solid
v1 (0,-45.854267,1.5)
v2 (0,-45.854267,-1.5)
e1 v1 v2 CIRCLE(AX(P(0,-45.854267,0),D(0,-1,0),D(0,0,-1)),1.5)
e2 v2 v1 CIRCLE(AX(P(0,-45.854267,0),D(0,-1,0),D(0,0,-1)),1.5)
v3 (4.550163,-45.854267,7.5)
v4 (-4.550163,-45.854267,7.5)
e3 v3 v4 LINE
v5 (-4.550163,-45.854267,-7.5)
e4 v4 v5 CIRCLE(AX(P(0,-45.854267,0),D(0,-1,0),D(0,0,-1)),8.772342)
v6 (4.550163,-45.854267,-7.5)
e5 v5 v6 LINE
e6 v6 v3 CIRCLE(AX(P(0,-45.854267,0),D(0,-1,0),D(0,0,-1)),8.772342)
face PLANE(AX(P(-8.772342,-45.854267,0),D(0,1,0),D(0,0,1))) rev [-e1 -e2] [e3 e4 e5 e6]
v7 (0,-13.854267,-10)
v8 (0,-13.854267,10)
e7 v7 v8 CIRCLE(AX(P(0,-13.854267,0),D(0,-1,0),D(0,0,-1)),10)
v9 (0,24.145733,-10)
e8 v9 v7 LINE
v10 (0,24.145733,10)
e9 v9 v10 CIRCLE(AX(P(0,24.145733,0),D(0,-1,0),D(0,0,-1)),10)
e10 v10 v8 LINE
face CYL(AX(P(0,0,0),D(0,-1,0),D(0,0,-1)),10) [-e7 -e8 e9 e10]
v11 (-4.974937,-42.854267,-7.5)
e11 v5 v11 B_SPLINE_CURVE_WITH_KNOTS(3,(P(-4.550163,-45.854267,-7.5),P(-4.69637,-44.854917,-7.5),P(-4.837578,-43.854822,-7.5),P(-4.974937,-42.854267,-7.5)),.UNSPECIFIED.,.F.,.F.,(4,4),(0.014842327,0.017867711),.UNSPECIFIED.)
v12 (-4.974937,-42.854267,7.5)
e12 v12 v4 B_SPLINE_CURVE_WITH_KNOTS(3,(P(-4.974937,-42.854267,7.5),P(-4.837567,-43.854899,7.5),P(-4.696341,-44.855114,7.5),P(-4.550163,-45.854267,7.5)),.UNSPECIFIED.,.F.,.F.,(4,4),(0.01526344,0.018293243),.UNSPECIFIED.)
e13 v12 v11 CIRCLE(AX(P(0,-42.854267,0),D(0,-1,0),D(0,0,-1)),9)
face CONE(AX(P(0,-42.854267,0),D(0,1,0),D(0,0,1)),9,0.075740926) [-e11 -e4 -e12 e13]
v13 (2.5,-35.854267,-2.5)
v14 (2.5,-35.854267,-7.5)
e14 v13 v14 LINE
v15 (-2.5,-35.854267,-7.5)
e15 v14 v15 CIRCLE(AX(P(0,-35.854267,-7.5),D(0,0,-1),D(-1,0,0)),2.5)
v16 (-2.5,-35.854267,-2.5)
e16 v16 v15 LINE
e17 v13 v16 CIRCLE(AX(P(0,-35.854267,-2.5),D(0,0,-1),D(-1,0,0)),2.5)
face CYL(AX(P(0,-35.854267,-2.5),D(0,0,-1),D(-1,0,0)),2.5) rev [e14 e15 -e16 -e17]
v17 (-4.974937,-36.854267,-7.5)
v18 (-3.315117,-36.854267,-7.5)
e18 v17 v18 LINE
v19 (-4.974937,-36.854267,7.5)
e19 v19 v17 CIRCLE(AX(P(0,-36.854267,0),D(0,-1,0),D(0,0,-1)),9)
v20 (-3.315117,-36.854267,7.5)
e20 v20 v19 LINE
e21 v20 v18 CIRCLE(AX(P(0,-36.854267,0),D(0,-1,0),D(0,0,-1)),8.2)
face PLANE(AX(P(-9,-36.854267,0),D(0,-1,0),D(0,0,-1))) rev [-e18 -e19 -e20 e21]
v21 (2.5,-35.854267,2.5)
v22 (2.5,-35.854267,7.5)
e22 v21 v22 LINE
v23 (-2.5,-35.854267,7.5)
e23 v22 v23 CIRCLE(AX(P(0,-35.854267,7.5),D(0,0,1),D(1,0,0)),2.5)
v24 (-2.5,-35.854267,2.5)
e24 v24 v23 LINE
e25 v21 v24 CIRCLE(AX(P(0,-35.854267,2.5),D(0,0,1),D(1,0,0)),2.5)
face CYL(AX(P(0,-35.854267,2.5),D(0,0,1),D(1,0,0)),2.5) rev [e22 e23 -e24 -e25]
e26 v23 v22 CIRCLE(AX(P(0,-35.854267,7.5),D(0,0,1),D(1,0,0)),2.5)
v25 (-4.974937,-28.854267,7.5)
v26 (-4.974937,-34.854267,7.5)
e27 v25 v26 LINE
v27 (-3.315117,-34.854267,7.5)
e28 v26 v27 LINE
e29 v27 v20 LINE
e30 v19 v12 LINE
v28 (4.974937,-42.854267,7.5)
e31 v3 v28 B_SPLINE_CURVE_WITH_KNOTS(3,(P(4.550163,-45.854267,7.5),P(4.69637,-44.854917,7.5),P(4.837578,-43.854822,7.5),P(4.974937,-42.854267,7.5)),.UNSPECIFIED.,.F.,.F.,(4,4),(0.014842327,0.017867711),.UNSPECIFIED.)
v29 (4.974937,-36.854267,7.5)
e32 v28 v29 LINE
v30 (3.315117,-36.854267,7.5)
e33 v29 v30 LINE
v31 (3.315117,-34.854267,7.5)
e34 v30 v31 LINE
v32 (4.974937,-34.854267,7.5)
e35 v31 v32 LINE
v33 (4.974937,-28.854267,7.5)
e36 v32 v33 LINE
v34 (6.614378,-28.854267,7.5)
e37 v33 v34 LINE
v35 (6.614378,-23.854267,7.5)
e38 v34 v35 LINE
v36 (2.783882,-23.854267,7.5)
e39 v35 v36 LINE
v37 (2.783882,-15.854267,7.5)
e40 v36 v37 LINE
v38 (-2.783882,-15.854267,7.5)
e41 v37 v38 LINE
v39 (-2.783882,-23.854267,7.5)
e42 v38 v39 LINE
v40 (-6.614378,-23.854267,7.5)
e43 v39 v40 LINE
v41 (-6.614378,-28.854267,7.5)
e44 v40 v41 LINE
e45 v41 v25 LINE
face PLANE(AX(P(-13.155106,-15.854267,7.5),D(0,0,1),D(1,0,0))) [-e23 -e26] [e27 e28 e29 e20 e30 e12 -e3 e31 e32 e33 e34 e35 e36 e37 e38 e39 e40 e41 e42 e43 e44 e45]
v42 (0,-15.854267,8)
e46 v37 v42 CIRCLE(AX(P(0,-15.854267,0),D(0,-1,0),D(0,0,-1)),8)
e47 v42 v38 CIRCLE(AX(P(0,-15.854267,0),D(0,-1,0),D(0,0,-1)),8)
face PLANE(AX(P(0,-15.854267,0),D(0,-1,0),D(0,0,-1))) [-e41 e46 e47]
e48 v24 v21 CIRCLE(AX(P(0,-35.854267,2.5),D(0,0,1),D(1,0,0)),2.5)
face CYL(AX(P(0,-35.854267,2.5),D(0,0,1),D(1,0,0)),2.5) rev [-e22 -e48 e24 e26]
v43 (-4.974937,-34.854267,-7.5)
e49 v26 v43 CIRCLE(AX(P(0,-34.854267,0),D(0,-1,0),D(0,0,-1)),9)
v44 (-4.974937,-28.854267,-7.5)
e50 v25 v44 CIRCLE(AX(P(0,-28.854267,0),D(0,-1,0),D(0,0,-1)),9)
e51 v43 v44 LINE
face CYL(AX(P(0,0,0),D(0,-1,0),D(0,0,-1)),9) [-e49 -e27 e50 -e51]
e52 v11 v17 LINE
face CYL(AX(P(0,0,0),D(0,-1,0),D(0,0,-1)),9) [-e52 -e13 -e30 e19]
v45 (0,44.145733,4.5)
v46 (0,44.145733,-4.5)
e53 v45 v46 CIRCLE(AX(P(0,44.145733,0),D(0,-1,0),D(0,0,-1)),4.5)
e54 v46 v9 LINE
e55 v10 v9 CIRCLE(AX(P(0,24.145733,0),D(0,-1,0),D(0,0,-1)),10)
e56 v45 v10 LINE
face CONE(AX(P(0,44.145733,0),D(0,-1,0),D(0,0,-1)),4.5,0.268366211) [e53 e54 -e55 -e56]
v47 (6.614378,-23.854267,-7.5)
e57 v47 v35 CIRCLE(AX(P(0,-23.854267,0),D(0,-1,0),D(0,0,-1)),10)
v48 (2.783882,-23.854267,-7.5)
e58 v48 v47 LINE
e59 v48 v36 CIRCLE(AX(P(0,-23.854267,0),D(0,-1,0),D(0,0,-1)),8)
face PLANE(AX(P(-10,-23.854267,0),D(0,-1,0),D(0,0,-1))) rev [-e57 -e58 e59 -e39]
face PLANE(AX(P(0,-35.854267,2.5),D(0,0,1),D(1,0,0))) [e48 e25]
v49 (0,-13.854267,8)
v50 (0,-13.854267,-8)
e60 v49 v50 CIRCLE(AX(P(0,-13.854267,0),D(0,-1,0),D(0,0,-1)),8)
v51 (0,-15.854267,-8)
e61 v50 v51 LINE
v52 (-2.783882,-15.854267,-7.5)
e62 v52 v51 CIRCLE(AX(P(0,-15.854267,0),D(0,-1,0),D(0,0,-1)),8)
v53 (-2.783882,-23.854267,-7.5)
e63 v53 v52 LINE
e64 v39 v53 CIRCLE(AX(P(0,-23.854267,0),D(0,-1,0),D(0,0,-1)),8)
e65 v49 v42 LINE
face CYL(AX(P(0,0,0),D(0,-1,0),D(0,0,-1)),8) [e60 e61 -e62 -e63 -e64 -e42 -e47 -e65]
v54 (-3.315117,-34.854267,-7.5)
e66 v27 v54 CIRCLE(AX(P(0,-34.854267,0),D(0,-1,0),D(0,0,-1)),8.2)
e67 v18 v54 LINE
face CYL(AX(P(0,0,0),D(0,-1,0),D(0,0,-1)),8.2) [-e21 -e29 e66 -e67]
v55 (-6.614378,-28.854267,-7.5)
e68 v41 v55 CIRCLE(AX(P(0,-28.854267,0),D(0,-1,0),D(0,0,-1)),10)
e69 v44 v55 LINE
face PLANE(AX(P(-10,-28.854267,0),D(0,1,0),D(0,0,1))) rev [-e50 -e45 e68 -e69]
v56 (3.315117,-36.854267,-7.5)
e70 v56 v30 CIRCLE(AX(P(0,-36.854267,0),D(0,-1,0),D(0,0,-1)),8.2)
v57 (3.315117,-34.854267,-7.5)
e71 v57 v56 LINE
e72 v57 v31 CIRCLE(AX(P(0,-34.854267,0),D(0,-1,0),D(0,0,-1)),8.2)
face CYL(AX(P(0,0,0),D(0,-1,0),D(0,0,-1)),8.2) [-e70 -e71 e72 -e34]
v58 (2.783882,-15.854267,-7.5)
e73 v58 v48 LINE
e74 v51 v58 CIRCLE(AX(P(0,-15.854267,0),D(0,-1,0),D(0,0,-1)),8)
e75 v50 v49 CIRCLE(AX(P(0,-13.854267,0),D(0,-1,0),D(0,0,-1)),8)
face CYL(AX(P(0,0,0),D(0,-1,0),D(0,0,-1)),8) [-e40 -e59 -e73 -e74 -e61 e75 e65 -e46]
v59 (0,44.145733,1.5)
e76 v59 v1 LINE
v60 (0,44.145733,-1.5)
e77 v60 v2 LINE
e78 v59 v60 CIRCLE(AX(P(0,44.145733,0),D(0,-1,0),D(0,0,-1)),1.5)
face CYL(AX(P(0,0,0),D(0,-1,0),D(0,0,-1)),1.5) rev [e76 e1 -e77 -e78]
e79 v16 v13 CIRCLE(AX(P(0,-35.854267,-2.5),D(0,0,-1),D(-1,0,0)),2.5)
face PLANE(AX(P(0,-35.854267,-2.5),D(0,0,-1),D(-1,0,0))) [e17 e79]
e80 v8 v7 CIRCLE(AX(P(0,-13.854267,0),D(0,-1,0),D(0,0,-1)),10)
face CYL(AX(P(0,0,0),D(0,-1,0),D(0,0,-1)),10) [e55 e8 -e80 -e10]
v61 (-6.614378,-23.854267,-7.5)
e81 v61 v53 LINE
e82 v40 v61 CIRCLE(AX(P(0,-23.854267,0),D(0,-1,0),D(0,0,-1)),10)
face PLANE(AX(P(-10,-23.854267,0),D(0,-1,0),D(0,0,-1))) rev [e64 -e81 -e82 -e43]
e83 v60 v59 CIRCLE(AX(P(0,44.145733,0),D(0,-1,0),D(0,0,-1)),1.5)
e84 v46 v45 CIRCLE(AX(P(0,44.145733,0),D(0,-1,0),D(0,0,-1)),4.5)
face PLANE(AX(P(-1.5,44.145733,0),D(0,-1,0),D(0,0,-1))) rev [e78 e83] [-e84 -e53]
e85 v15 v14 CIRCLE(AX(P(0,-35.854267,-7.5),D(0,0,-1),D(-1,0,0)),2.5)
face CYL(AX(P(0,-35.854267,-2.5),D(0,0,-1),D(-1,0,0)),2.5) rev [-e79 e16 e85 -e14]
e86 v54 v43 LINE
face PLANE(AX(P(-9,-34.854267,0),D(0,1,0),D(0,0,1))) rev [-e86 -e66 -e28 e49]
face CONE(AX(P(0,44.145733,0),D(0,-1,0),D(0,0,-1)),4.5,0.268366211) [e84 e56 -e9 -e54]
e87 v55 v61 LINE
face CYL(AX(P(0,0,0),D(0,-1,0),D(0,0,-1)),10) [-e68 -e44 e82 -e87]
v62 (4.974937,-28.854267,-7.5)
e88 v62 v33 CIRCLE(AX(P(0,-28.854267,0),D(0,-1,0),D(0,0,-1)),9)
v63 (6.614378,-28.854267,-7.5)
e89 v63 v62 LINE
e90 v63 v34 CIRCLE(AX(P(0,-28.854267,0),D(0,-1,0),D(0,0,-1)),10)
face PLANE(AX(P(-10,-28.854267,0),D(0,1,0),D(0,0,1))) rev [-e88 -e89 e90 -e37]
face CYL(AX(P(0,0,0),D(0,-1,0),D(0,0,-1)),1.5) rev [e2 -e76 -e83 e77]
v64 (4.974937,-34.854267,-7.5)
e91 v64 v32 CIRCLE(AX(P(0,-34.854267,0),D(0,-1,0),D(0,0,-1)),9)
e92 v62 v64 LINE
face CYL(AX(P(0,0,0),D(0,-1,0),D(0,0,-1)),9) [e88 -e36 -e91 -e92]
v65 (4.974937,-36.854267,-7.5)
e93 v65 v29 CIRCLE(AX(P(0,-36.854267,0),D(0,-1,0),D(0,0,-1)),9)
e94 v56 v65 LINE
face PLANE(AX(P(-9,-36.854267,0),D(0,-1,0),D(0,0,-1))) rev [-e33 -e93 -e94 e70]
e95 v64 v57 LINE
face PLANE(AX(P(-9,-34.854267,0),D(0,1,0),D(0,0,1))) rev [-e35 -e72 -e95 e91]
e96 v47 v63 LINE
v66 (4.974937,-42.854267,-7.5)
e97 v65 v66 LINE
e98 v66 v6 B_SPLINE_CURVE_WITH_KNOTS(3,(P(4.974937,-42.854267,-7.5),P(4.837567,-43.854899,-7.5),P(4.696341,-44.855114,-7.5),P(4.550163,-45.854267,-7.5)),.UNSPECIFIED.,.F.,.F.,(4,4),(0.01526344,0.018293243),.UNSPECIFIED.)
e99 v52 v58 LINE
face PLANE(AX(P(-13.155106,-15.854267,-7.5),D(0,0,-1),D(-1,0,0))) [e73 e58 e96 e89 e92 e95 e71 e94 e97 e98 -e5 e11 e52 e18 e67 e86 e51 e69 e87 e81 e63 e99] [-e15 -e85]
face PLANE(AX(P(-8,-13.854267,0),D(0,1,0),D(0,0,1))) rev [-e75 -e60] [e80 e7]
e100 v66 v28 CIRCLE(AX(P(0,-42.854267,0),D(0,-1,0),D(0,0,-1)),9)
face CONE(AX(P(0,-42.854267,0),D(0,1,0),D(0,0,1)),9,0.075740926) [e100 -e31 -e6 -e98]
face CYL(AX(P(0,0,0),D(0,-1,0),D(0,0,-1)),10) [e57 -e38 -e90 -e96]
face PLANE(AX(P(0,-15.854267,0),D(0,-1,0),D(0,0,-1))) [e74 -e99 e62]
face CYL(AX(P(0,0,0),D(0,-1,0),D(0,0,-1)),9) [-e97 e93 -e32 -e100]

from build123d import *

# Parameters (mm, degrees)
SKETCH2_OUTSIDE_W   = 40.868
SKETCH2_OUTSIDE_H   = 40.868
SKETCH2_OUTSIDE_W_2 = 26.310212334
SKETCH2_OUTSIDE_H_2 = 15
CUT_EXTRUDE1_DEPTH  = 30
SKETCH3_R           = 2.5
CUT_EXTRUDE2_DEPTH  = 5
CUT_EXTRUDE3_START  = -5
SKETCH5_R           = 2.5
CUT_EXTRUDE3_DEPTH  = 5


with BuildPart() as part:
    # Sketch1 → Revolve1 (revolve)
    with BuildSketch(Plane.XY, mode=Mode.PRIVATE) as revolve1_sk:
        Polygon((-1.5, -45.854266644), (-1.5, 44.145733356), (-4.5, 44.145733356), (-10, 24.145733356), (-10, -13.854266644), (-8, -13.854266644), (-8, -23.854266644), (-10, -23.854266644), (-10, -28.854266644), (-9, -28.854266644), (-9, -34.854266644), (-8.2, -34.854266644), (-8.2, -36.854266644), (-9, -36.854266644), (-9, -42.854266644), (-8.77234172, -45.854266644), align=None)
    revolve(revolve1_sk.sketch.rotate(Axis((0, 0, 0), (0, 1, 0)), 270), axis=Axis((0, 0, 0), (0, 1, 0)))

    # Sketch2 outside → Cut-Extrude1 (cut)
    with BuildSketch(Plane(origin=(0, -45.854266644, 0), x_dir=(-1, 0, 0), z_dir=(0, -1, 0))):
        Rectangle(SKETCH2_OUTSIDE_W, SKETCH2_OUTSIDE_H)
        Rectangle(SKETCH2_OUTSIDE_W_2, SKETCH2_OUTSIDE_H_2, mode=Mode.SUBTRACT)
    extrude(amount=-CUT_EXTRUDE1_DEPTH, mode=Mode.SUBTRACT)

    # Sketch3 → Cut-Extrude2 (cut)
    with BuildSketch(Plane.XY.offset(7.5)):
        with Locations((0, -35.854266644)):
            Circle(SKETCH3_R)
    extrude(amount=-CUT_EXTRUDE2_DEPTH, mode=Mode.SUBTRACT)

    # Sketch5 → Cut-Extrude3 (cut)
    with BuildSketch(Plane(origin=(0, 0, -7.5), x_dir=(-1, 0, 0), z_dir=(0, 0, -1)).offset(CUT_EXTRUDE3_START)):
        with Locations(Location((0, -35.854266644, 0), (0, 0, 180))):
            Circle(SKETCH5_R)
    extrude(amount=CUT_EXTRUDE3_DEPTH, mode=Mode.SUBTRACT)


solid = part.part
